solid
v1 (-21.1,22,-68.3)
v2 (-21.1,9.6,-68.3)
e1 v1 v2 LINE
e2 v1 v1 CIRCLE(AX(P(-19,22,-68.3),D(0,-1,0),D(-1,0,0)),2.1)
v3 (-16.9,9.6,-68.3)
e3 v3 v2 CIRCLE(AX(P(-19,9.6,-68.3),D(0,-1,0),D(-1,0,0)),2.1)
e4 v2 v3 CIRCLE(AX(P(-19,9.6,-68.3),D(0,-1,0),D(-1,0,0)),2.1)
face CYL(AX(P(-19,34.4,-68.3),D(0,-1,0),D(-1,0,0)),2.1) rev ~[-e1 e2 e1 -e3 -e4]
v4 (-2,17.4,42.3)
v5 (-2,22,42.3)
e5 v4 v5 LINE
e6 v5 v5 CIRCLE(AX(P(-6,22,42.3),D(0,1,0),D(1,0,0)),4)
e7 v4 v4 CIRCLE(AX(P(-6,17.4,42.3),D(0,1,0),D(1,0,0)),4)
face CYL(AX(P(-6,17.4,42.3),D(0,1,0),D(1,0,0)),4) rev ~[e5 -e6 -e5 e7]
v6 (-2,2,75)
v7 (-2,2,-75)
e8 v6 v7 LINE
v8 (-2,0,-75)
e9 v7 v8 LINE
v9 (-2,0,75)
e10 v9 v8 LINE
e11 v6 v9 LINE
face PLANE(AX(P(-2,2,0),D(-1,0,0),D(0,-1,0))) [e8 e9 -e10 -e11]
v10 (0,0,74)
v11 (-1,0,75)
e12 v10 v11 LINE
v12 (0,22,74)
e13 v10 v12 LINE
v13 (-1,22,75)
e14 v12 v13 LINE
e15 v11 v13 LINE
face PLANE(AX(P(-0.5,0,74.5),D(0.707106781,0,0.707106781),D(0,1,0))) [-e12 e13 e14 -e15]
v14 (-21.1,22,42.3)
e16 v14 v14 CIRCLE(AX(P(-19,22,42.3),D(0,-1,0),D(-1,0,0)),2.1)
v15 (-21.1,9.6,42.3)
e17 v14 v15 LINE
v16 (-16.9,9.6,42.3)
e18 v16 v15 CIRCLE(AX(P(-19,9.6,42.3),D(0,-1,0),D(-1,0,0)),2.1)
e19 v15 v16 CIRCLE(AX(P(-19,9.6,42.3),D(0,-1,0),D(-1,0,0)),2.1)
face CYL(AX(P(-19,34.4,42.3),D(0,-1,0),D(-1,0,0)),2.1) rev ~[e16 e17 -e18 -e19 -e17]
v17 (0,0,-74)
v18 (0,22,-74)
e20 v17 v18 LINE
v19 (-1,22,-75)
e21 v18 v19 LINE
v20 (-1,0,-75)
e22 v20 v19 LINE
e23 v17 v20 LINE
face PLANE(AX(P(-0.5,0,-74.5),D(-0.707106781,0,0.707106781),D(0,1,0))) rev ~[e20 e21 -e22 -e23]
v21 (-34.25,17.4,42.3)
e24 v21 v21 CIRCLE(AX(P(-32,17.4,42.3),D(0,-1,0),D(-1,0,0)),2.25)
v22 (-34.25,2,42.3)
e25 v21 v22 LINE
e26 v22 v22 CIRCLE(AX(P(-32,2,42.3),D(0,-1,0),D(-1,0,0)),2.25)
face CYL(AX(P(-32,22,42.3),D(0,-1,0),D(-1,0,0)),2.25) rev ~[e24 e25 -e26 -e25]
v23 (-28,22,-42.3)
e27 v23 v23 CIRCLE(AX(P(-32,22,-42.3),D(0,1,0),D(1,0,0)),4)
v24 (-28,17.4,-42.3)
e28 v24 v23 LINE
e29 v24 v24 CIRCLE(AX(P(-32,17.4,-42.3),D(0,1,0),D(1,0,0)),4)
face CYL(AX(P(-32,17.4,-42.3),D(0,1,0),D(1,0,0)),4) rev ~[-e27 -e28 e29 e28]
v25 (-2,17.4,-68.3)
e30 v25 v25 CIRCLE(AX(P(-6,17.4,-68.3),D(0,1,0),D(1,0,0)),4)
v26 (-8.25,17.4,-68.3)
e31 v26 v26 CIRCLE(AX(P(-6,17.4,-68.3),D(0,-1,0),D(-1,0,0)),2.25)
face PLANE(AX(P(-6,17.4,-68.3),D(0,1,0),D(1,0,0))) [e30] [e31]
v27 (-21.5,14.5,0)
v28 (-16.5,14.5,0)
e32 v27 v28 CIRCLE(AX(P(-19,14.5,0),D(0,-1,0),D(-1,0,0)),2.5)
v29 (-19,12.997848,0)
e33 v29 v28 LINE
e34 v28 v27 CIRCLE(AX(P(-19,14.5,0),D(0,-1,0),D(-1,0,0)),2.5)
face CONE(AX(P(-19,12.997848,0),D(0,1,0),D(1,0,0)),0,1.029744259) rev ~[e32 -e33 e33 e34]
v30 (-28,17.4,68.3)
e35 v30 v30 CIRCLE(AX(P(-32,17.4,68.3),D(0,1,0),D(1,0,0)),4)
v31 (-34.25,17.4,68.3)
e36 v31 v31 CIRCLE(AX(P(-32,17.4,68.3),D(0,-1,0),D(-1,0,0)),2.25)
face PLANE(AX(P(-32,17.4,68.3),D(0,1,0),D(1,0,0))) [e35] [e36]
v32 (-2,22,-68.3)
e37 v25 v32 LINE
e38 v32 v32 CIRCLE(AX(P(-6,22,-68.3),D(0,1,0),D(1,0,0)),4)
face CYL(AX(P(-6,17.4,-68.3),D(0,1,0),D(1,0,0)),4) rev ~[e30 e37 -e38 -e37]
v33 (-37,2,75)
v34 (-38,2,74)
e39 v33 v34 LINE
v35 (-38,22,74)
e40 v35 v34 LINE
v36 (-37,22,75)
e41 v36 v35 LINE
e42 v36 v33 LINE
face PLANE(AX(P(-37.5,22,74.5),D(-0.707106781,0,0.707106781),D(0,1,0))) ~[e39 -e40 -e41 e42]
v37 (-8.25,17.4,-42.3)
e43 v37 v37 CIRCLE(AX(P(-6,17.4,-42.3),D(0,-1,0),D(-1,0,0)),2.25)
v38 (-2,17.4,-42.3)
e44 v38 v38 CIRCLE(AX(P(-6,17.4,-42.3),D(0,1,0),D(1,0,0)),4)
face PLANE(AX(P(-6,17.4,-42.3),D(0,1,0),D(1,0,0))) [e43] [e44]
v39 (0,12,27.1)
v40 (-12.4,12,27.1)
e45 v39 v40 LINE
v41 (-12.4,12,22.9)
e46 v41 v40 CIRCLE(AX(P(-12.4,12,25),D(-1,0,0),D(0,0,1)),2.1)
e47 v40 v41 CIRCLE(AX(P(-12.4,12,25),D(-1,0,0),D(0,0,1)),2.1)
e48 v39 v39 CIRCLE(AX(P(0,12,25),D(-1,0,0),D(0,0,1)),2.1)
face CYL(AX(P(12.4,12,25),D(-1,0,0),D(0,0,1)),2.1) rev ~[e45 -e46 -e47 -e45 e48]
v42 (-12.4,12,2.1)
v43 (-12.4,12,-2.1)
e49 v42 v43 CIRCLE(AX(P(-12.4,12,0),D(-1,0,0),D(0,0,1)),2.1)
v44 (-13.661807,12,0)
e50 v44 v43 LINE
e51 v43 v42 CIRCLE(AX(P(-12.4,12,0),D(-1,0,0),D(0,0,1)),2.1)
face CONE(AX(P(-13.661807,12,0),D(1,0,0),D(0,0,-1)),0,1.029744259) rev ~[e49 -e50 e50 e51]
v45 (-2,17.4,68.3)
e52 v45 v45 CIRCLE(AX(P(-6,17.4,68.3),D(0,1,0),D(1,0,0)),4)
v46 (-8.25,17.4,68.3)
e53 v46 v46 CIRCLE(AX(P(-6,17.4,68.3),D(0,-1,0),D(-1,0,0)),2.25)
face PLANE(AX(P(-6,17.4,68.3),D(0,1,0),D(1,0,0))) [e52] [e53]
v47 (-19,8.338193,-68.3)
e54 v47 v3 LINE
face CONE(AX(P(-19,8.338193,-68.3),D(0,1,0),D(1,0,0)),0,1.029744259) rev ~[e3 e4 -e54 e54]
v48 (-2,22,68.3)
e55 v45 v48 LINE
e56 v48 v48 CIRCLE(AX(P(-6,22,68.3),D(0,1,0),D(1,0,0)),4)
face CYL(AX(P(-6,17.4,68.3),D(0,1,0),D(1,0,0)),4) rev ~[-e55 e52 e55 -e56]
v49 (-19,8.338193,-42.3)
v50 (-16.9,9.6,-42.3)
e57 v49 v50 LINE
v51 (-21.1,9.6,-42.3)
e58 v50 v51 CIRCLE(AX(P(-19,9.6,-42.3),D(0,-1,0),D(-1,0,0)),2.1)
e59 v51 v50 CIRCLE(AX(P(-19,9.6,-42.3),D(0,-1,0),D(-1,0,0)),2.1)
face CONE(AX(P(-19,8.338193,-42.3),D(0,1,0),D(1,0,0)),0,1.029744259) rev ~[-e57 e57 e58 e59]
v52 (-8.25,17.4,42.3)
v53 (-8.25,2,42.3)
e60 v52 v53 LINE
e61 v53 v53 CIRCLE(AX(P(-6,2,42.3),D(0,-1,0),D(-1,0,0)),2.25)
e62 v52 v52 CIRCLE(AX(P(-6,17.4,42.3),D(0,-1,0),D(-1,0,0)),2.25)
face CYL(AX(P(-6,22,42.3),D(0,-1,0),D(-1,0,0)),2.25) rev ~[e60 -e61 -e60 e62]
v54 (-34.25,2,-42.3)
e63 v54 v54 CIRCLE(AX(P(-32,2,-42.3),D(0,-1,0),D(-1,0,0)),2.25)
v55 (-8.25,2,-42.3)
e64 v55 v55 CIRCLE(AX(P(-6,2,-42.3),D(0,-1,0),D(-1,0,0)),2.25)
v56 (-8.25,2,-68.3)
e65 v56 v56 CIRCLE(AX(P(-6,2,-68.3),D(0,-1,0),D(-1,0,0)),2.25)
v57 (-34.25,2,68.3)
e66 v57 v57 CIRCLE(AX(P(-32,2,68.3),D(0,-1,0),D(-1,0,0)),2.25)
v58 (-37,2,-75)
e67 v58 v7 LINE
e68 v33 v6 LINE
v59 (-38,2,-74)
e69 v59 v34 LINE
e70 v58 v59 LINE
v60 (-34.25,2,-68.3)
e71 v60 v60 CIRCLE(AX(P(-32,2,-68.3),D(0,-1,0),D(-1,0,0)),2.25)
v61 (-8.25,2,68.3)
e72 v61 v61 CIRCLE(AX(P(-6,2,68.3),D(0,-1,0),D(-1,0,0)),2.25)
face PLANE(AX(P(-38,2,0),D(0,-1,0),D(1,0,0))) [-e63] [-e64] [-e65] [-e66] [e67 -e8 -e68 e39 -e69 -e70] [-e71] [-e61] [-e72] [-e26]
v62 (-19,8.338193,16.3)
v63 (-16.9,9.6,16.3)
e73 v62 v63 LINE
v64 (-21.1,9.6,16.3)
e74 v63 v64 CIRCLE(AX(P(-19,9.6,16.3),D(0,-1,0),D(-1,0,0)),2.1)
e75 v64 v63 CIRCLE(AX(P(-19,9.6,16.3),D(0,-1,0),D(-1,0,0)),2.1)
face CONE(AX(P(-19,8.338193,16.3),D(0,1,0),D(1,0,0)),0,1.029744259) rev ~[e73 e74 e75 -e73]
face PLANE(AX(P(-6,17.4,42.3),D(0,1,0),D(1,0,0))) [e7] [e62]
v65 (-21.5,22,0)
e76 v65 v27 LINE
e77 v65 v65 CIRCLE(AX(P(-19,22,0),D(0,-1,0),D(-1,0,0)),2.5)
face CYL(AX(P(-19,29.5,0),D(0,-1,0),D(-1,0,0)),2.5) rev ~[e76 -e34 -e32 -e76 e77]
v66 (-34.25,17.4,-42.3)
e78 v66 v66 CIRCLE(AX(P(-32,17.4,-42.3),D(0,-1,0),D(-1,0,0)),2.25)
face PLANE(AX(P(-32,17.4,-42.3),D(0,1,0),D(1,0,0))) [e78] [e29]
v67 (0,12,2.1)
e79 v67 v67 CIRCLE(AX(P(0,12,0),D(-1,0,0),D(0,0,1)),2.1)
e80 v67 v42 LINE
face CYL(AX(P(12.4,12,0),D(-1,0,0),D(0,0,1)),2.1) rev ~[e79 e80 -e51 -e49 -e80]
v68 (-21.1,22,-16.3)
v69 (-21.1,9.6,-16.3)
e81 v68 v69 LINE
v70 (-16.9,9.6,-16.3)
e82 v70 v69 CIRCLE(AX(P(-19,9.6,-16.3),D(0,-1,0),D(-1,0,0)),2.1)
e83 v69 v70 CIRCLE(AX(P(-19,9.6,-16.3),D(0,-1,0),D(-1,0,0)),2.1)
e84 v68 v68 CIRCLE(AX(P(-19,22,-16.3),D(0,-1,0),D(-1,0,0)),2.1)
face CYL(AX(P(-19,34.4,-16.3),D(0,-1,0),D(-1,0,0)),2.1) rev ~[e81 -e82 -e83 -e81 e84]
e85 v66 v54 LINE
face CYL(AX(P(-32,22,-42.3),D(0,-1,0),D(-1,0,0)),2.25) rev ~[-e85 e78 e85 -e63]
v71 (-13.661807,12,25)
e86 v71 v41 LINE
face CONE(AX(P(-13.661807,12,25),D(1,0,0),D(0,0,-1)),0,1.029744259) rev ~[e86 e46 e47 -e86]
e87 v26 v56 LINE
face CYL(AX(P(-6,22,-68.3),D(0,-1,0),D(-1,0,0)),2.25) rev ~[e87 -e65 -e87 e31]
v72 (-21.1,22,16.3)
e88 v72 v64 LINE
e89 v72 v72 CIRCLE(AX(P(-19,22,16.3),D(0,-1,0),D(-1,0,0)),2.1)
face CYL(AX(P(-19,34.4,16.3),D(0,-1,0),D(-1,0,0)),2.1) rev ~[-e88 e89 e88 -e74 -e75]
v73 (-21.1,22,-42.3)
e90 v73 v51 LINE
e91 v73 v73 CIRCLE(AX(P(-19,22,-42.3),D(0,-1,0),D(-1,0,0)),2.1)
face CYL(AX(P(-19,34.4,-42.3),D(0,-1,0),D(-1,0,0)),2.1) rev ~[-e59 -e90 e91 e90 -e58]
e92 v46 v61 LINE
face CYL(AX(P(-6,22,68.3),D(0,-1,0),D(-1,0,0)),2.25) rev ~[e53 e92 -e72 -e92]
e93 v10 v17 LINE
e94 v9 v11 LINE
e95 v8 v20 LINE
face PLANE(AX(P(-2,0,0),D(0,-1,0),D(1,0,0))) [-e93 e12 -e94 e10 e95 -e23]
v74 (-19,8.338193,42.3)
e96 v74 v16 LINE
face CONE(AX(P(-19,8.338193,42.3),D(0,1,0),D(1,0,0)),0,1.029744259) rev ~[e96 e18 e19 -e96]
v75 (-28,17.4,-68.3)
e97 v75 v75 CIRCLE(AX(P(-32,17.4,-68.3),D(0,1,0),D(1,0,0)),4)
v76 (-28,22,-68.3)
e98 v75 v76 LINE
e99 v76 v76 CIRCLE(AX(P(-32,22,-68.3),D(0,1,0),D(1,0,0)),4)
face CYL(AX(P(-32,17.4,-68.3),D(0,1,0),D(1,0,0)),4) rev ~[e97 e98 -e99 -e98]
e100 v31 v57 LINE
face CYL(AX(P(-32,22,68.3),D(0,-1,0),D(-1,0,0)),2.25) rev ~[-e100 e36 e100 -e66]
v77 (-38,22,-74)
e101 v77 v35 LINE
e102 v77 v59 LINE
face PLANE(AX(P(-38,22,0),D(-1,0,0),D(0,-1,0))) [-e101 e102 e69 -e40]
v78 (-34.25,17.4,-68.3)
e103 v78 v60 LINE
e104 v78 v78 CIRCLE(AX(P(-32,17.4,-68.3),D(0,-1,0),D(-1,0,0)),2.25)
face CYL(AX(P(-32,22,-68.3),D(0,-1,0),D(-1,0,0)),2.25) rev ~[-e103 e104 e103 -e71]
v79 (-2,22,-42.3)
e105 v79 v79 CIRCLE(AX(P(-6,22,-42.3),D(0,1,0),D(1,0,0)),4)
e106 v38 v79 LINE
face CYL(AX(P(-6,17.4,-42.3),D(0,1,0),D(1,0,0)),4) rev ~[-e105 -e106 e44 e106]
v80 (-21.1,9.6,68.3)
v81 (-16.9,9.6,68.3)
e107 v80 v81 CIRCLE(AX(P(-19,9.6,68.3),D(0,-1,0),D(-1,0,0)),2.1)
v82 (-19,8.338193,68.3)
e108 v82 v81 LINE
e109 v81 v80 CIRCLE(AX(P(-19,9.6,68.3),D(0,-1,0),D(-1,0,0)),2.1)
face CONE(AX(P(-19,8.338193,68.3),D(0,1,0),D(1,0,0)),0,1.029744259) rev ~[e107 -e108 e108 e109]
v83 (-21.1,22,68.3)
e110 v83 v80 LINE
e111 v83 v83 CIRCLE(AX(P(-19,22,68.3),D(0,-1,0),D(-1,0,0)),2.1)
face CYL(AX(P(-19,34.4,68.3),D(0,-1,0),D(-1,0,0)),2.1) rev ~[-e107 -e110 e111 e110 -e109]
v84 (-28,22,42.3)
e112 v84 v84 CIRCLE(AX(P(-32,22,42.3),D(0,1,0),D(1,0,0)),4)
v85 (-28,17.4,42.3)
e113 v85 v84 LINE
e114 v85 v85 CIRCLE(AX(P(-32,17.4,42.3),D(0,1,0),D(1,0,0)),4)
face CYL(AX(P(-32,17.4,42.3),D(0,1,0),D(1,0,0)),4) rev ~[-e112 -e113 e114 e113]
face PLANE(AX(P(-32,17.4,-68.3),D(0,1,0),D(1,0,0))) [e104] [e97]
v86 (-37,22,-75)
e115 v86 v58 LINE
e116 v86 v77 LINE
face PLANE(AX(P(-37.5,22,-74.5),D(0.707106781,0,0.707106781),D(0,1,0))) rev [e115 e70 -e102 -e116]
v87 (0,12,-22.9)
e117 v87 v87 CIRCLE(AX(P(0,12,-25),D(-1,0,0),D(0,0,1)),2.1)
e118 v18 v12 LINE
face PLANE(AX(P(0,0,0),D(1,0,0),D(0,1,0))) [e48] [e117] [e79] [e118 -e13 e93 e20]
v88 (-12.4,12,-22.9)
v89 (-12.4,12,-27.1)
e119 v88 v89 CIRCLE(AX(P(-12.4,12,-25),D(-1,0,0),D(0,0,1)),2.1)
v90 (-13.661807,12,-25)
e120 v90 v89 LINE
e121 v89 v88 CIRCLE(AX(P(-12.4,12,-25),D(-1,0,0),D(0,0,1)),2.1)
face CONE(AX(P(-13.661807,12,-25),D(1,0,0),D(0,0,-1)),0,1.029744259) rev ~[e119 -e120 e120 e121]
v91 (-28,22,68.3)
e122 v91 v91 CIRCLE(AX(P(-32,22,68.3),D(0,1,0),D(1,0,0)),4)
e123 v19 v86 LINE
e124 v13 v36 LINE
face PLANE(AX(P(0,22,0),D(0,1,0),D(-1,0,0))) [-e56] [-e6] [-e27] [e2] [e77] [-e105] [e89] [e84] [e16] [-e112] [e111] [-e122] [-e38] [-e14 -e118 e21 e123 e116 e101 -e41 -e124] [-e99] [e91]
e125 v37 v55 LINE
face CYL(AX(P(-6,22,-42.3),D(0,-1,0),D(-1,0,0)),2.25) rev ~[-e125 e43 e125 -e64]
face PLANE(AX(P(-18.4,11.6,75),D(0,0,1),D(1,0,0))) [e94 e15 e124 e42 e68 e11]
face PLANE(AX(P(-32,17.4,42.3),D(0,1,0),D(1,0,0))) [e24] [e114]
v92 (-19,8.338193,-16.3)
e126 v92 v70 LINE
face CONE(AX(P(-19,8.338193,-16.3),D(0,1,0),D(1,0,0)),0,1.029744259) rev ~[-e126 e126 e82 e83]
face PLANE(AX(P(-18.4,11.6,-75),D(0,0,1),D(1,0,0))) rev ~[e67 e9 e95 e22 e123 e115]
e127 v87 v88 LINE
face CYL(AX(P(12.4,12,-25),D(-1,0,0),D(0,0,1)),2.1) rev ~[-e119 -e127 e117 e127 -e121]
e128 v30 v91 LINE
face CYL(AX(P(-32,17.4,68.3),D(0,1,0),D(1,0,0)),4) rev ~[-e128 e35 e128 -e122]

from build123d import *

# Parameters (mm, degrees)
BOSS_EXTRUDE1_DEPTH                                = 75
HOLE_SIZE_SOCKET_HEAD_CAP_SCREW_TYPE_1_D           = 4.5
HOLE_SIZE_SOCKET_HEAD_CAP_SCREW_TYPE_1_CBORE_D     = 8
HOLE_SIZE_SOCKET_HEAD_CAP_SCREW_TYPE_1_CBORE_DEPTH = 4.6
M5_TAPPED_HOLE1_D                                  = 4.2
M5_TAPPED_HOLE1_DEPTH                              = 12.4
M5_TAPPED_HOLE1_TIP                                = 1.2618073
M5_TAPPED_HOLE2_D                                  = 4.2
M5_TAPPED_HOLE2_DEPTH                              = 12.4
M5_TAPPED_HOLE2_TIP                                = 1.2618073
CHAMFER1_SIZE                                      = 1
DOWEL_HOLE1_D                                      = 5
DOWEL_HOLE1_DEPTH                                  = 7.5
DOWEL_HOLE1_TIP                                    = 1.502151548


with BuildPart() as part:
    # Sketch1 → Boss-Extrude1 (new, symmetric)
    with BuildSketch(Plane.XY):
        Polygon((0, 0), (0, 22), (-38, 22), (-38, 2), (-2, 2), (-2, 0), align=None)
    extrude(amount=BOSS_EXTRUDE1_DEPTH, both=True)

    # Hole size (socket head cap screw type)1 (through all)
    with Locations(Plane(origin=(0, 22, 0), x_dir=(1, 0, 0), z_dir=(0, 1, 0))):
        with Locations((-32, -68.3), (-32, 68.3), (-6, 42.3), (-32, 42.3), (-6, 68.3), (-6, -68.3), (-6, -42.3), (-32, -42.3)):
            CounterBoreHole(HOLE_SIZE_SOCKET_HEAD_CAP_SCREW_TYPE_1_D / 2, HOLE_SIZE_SOCKET_HEAD_CAP_SCREW_TYPE_1_CBORE_D / 2, HOLE_SIZE_SOCKET_HEAD_CAP_SCREW_TYPE_1_CBORE_DEPTH)

    # M5 Tapped Hole1
    with Locations(Plane(origin=(0, 0, 0), x_dir=(0, 0, -1), z_dir=(1, 0, 0))):
        with Locations((0, 12), (-25, 12), (25, 12)):
            Hole(M5_TAPPED_HOLE1_D / 2, depth=M5_TAPPED_HOLE1_DEPTH)
            with Locations((0, 0, -(M5_TAPPED_HOLE1_DEPTH + M5_TAPPED_HOLE1_TIP / 2))):  # 118° drill point
                Cone(0, M5_TAPPED_HOLE1_D / 2, M5_TAPPED_HOLE1_TIP, mode=Mode.SUBTRACT)

    # M5 Tapped Hole2
    with Locations(Plane(origin=(0, 22, 0), x_dir=(1, 0, 0), z_dir=(0, 1, 0))):
        with Locations((-19, -16.3), (-19, 68.3), (-19, 42.3), (-19, -42.3), (-19, -68.3), (-19, 16.3)):
            Hole(M5_TAPPED_HOLE2_D / 2, depth=M5_TAPPED_HOLE2_DEPTH)
            with Locations((0, 0, -(M5_TAPPED_HOLE2_DEPTH + M5_TAPPED_HOLE2_TIP / 2))):  # 118° drill point
                Cone(0, M5_TAPPED_HOLE2_D / 2, M5_TAPPED_HOLE2_TIP, mode=Mode.SUBTRACT)

    # Chamfer1
    chamfer1_edges = [part.edges().sort_by_distance(p)[0] for p in [
        (-38, 12, 75),
        (-38, 12, -75),
        (0, 11, -75),
        (0, 11, 75),
    ]]
    chamfer(chamfer1_edges, length=CHAMFER1_SIZE)

    # Dowel Hole1
    with Locations(Plane(origin=(0, 22, 0), x_dir=(1, 0, 0), z_dir=(0, 1, 0))):
        with Locations((-19, 0)):
            Hole(DOWEL_HOLE1_D / 2, depth=DOWEL_HOLE1_DEPTH)
            with Locations((0, 0, -(DOWEL_HOLE1_DEPTH + DOWEL_HOLE1_TIP / 2))):  # 118° drill point
                Cone(0, DOWEL_HOLE1_D / 2, DOWEL_HOLE1_TIP, mode=Mode.SUBTRACT)


solid = part.part
